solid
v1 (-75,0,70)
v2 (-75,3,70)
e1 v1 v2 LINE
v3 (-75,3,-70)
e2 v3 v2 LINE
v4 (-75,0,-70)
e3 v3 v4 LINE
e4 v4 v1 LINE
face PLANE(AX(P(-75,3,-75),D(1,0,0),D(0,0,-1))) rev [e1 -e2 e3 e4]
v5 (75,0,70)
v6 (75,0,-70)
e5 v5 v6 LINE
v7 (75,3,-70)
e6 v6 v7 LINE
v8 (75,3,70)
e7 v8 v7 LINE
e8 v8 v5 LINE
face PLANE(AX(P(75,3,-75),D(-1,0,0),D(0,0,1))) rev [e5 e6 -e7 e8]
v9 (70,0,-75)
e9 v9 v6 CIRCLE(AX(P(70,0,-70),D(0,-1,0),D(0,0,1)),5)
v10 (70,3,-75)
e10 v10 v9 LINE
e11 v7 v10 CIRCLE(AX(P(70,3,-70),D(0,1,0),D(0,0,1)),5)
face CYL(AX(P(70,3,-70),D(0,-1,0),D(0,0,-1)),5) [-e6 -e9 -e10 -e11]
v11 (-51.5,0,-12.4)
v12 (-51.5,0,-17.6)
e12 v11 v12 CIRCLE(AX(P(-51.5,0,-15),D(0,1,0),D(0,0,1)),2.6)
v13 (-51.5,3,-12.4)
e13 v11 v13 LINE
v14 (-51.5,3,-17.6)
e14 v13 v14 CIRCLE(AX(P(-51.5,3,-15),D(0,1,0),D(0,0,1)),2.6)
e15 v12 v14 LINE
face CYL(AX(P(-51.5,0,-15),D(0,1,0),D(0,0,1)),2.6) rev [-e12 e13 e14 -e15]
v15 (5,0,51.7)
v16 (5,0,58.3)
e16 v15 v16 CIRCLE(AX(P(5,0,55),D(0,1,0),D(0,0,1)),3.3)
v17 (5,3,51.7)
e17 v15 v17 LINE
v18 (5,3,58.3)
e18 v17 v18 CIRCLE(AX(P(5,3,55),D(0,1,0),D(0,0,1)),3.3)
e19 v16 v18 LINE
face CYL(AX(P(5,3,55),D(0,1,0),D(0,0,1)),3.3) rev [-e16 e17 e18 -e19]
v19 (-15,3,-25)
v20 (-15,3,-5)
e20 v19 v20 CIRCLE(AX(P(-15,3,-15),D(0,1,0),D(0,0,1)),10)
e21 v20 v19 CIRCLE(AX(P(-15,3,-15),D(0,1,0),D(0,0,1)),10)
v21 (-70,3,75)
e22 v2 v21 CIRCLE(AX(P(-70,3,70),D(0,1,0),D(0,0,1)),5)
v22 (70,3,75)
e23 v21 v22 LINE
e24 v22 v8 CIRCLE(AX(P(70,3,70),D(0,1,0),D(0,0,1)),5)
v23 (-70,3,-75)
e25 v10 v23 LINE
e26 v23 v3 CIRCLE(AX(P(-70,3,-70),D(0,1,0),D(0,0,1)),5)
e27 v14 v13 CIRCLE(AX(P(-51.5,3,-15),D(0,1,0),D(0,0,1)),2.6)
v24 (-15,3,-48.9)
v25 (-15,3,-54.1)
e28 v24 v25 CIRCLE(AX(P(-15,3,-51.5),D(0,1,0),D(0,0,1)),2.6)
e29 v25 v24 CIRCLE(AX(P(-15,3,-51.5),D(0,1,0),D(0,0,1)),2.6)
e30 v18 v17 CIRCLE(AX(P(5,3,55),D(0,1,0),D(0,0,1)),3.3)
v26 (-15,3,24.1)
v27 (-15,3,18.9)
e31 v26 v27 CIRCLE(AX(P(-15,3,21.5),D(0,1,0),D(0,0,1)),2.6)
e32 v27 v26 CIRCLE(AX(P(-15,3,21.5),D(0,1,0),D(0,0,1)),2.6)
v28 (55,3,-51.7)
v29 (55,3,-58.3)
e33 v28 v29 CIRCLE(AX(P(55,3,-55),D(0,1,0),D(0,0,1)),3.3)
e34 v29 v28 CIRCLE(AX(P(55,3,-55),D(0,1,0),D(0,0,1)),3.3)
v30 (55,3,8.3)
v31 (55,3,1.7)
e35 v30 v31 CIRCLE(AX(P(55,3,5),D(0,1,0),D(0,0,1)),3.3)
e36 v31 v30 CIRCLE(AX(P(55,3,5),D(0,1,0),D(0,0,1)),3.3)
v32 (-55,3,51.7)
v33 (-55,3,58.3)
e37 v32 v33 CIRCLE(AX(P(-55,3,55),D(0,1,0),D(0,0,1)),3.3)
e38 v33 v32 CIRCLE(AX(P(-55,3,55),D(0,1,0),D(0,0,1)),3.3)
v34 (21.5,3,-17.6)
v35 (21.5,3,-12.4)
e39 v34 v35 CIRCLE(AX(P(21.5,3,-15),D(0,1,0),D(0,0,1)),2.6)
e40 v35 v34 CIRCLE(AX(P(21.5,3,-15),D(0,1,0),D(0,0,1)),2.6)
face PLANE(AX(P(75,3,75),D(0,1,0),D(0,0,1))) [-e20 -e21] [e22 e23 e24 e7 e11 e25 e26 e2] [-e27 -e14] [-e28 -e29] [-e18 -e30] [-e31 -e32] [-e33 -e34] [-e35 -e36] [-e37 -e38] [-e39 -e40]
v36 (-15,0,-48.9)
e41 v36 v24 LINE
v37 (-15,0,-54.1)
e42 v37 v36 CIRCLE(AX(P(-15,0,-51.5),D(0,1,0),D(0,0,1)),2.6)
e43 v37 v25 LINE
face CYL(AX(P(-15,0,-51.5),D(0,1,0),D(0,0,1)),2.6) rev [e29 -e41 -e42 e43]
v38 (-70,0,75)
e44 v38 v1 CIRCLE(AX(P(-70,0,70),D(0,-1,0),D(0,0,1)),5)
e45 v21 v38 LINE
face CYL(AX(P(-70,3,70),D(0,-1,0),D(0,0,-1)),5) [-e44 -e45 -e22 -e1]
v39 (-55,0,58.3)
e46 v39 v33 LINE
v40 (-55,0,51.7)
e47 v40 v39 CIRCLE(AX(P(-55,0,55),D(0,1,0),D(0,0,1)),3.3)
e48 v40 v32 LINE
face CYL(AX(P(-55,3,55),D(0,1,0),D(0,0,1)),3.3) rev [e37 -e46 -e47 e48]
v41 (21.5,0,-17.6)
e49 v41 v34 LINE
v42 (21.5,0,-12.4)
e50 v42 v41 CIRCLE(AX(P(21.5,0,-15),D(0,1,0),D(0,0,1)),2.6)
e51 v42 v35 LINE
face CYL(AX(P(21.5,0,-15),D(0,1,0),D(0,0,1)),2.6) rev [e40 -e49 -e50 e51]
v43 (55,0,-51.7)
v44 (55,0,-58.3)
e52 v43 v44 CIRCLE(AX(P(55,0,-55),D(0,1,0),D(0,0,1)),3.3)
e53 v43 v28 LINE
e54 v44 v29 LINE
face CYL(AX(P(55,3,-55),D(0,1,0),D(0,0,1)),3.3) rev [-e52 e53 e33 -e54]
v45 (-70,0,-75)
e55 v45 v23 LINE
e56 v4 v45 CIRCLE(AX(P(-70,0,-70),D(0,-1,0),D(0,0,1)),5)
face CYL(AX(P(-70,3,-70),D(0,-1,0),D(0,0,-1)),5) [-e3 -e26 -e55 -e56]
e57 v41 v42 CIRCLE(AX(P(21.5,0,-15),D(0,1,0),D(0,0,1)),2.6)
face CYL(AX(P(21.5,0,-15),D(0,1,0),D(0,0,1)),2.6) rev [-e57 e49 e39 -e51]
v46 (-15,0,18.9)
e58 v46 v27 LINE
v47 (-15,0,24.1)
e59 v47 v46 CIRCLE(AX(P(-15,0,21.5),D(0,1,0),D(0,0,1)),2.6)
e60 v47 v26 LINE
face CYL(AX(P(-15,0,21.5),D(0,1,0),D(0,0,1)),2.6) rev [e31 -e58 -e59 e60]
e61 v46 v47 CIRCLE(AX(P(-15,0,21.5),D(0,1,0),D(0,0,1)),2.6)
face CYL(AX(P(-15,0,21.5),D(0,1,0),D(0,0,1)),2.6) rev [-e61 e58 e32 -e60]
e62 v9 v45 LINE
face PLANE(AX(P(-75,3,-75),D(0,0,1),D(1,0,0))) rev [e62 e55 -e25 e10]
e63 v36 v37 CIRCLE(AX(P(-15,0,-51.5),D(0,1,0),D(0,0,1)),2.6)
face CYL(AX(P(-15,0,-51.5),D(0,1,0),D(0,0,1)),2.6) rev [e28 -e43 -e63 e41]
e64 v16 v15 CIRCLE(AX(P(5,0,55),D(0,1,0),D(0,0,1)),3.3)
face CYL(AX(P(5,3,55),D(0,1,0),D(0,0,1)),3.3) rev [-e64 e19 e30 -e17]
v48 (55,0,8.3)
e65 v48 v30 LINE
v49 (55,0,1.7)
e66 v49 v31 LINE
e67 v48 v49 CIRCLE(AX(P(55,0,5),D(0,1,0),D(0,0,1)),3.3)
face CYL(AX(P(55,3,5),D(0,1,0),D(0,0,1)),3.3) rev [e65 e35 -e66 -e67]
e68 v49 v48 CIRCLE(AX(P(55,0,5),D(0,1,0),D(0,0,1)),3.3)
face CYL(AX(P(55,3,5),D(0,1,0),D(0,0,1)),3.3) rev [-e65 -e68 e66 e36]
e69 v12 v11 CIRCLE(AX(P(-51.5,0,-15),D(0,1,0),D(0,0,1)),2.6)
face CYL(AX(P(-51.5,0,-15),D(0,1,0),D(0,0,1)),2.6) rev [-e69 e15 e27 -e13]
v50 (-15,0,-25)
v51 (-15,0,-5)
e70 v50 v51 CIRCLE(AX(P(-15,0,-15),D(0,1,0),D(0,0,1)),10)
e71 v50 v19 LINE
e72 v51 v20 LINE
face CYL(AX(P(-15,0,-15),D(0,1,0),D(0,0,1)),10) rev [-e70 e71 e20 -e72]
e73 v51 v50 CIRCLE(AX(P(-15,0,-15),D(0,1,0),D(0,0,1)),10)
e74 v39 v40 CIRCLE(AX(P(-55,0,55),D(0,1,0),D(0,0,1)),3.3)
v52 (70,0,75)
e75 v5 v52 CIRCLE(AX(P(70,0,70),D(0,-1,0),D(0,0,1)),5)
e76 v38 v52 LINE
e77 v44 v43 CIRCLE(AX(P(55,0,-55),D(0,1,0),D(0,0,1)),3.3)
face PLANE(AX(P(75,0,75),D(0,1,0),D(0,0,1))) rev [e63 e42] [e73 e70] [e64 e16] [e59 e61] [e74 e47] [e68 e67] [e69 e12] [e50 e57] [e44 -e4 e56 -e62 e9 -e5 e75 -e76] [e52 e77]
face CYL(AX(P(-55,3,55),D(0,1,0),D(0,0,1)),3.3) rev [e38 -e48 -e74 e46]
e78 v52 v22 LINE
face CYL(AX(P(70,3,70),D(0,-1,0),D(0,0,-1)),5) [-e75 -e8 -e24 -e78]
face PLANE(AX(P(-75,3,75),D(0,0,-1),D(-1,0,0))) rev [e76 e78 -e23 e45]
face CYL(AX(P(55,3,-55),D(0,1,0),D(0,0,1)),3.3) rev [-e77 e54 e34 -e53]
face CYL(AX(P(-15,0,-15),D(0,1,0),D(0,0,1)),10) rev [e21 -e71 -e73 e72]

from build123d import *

# Parameters (mm, degrees)
SKETCH_1_W              = 150
SKETCH_1_H              = 150
EXTRUDE_1_DEPTH         = 3
HOLE_WIZARD_6_6_6_6_1_D = 6.6
FILLET_1_R              = 5
SKETCH_4_R              = 10
SKETCH_4_R_2            = 2.6
CUT_EXTRUDE_1_DEPTH     = 107.108435103


with BuildPart() as part:
    # 草图1 → 凸台-拉伸1 (new body)
    with BuildSketch(Plane(origin=(0, 0, 0), x_dir=(1, 0, 0), z_dir=(0, 1, 0))):
        Rectangle(SKETCH_1_W, SKETCH_1_H)
    extrude(amount=EXTRUDE_1_DEPTH)

    # Ø6.6 (6.6) 直径孔1 (through all)
    with Locations(Plane(origin=(0, 3, 0), x_dir=(-1, 0, 0), z_dir=(0, 1, 0))):
        with Locations((-55, 5), (-5, 55), (55, 55), (-55, -55)):
            Hole(HOLE_WIZARD_6_6_6_6_1_D / 2)

    # 圆角1
    fillet_1_edges = [part.edges().sort_by_distance(p)[0] for p in [
        (75, 1.5, 75),
        (-75, 1.5, 75),
        (-75, 1.5, -75),
        (75, 1.5, -75),
    ]]
    fillet(fillet_1_edges, radius=FILLET_1_R)

    # 草图4 → 切除-拉伸1 (cut, through all)
    with BuildSketch(Plane(origin=(0, 3, 0), x_dir=(1, 0, 0), z_dir=(0, 1, 0))):
        with Locations(Location((-15, 15, 0), (0, 0, 270))):
            Circle(SKETCH_4_R)
        with Locations(Location((-15, 51.5, 0), (0, 0, 270))):
            Circle(SKETCH_4_R_2)
        with Locations(Location((21.5, 15, 0), (0, 0, 270))):
            Circle(SKETCH_4_R_2)
        with Locations(Location((-15, -21.5, 0), (0, 0, 270))):
            Circle(SKETCH_4_R_2)
        with Locations(Location((-51.5, 15, 0), (0, 0, 270))):
            Circle(SKETCH_4_R_2)
    extrude(amount=-CUT_EXTRUDE_1_DEPTH, mode=Mode.SUBTRACT)


solid = part.part
